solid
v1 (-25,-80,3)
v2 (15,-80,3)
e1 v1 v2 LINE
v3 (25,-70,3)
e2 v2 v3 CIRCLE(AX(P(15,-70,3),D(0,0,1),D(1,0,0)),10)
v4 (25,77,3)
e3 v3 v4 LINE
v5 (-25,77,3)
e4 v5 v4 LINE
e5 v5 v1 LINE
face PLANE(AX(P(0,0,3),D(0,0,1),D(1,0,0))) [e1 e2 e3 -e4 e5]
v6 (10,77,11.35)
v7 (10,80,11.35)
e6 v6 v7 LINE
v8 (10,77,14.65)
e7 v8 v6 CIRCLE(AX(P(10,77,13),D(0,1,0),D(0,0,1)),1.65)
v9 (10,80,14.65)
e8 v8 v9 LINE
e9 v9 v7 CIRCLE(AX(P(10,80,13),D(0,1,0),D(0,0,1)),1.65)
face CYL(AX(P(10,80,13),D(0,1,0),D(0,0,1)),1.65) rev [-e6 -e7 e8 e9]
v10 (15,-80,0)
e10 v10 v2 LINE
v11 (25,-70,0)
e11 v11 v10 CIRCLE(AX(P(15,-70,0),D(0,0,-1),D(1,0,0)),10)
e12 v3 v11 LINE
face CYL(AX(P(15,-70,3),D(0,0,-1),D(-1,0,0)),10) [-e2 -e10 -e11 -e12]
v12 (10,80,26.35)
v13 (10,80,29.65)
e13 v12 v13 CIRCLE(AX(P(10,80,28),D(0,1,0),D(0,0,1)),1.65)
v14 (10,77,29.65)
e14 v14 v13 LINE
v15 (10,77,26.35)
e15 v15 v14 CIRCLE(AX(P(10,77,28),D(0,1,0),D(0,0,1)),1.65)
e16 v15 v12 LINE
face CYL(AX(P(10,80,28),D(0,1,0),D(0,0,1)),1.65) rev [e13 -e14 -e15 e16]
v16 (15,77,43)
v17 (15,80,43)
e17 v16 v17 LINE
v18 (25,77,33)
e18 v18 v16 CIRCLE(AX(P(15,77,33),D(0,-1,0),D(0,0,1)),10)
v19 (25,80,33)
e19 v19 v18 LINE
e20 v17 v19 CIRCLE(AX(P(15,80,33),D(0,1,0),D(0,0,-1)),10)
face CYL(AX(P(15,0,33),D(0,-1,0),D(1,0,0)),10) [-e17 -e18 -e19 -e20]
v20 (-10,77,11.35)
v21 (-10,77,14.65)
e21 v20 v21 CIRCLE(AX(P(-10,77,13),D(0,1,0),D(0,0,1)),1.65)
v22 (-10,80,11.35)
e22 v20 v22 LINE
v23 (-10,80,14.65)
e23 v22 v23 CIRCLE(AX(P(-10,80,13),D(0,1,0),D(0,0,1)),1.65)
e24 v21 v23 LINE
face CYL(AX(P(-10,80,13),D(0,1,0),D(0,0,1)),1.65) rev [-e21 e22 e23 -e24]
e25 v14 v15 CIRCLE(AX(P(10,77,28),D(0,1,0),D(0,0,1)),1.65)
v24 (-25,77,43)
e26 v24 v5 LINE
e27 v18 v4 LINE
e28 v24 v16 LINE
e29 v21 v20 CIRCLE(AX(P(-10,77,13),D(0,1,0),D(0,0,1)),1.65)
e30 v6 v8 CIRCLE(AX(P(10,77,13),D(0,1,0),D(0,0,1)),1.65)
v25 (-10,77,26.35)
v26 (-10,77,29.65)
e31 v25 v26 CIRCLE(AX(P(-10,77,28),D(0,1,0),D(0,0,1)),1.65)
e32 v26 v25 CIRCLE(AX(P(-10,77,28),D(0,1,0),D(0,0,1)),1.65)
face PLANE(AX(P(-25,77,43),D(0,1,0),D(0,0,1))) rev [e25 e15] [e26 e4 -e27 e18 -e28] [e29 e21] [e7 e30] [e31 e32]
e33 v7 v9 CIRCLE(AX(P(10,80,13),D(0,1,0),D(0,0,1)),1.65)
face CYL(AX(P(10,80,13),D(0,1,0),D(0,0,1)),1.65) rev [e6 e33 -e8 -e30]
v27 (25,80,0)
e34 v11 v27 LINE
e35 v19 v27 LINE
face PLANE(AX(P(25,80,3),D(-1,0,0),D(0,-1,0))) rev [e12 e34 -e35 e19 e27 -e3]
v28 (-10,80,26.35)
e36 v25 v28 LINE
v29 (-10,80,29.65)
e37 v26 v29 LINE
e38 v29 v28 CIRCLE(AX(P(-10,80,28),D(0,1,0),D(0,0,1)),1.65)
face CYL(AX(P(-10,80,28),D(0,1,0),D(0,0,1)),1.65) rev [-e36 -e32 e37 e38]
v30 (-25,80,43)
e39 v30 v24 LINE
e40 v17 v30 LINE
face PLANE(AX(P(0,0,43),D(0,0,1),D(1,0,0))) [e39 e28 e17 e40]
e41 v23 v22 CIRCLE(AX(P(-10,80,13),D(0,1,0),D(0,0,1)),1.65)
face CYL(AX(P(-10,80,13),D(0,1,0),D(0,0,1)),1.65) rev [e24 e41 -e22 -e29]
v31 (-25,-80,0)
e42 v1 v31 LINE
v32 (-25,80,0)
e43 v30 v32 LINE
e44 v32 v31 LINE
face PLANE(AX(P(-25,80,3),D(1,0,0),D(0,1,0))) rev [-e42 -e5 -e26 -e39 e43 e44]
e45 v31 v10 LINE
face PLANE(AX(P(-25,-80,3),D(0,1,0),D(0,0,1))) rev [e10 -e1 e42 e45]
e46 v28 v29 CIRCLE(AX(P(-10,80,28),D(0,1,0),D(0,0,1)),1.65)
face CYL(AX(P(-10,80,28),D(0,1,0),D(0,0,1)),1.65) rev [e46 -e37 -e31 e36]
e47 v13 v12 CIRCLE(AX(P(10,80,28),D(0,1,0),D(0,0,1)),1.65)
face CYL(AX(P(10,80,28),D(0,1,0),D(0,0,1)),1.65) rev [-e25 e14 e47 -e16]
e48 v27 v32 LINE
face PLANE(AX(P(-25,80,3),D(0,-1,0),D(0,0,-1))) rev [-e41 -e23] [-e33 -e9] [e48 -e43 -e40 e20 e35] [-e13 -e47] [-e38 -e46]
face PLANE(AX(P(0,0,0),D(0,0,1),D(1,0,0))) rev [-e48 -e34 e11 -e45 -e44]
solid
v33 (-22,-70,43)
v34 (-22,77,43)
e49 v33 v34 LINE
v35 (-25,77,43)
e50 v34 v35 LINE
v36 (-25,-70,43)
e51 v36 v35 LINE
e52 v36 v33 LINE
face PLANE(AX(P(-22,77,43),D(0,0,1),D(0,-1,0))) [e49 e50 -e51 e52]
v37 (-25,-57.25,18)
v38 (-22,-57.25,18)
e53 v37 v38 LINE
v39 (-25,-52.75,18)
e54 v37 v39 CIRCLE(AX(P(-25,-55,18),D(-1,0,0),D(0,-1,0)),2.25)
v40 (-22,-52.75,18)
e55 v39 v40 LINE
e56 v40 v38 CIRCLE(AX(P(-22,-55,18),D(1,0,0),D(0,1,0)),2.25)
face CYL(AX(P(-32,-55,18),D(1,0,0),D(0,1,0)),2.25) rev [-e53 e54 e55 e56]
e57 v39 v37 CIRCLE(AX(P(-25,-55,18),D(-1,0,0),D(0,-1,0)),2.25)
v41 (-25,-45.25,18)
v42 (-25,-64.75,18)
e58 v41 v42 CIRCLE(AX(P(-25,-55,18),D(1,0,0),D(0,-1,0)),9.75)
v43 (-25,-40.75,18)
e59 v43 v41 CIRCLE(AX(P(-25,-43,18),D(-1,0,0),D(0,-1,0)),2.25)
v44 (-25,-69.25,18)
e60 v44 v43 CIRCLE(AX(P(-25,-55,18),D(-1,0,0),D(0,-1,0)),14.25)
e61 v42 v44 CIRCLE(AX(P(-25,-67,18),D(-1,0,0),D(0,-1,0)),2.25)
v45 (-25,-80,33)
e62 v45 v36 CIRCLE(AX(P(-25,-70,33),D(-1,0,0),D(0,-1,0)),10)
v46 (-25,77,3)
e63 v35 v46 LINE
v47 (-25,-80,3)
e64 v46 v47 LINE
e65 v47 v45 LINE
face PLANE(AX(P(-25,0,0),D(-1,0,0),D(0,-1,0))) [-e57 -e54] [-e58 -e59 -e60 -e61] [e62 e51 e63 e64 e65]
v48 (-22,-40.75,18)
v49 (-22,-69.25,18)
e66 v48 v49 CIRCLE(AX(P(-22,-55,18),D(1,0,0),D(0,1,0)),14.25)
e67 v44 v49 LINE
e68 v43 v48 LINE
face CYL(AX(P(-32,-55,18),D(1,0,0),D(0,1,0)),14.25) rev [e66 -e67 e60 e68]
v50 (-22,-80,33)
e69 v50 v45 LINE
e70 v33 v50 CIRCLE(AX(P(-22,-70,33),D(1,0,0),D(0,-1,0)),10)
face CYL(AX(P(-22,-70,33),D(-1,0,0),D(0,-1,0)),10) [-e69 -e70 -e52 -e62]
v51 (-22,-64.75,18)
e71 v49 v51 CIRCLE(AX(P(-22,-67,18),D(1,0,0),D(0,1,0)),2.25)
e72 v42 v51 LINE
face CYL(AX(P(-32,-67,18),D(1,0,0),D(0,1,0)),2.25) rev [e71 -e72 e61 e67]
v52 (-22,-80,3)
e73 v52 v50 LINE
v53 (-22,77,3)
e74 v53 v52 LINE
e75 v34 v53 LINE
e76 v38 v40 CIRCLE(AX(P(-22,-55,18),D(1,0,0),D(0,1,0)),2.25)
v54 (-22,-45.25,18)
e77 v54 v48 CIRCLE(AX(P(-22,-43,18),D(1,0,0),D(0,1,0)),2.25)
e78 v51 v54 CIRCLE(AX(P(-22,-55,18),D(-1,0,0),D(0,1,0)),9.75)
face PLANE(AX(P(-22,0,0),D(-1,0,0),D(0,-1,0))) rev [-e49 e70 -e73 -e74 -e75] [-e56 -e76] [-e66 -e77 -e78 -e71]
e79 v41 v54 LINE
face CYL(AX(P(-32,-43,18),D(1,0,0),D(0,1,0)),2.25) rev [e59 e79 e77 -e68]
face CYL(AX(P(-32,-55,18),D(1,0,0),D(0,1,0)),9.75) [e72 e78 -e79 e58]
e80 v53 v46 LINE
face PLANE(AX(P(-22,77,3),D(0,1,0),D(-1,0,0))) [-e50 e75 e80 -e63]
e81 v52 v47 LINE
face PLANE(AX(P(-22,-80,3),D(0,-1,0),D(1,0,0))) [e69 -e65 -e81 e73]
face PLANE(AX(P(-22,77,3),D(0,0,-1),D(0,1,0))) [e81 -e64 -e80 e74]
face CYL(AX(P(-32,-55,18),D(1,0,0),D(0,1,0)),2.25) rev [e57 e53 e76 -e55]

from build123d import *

# Parameters (mm, degrees)
SKETCH_1_W                  = 50
SKETCH_1_H                  = 160
EXTRUDE_1_DEPTH             = 3
SKETCH_2_W                  = 50
SKETCH_2_H                  = 3
EXTRUDE_2_DEPTH             = 40
SKETCH_5_W                  = 40
SKETCH_5_H                  = 157
EXTRUDE_3_DEPTH             = 3
SKETCH_6_R                  = 2.25
CUT_EXTRUDE_1_DEPTH         = 10
SKETCH_8_W                  = 1.65
SKETCH_8_H                  = 160
HOLE_WIZARD_M4_1_AT_2_COUNT = 2
HOLE_WIZARD_M4_1_AT_2_PITCH = 20
HOLE_WIZARD_M4_1_AT_3_COUNT = 2
HOLE_WIZARD_M4_1_AT_3_PITCH = 15
HOLE_WIZARD_M4_1_AT_4_COUNT = 2
HOLE_WIZARD_M4_1_AT_4_PITCH = 25
FILLET_1_R                  = 10
FILLET_2_R                  = 10


with BuildPart() as part:
    # 草图1 → 凸台-拉伸1 (new body)
    with BuildSketch(Plane.XY):
        Rectangle(SKETCH_1_W, SKETCH_1_H)
    extrude(amount=EXTRUDE_1_DEPTH)

    # 草图2 → 凸台-拉伸2 (add)
    with BuildSketch(Plane.XY.offset(3)):
        with Locations((0, 78.5)):
            Rectangle(SKETCH_2_W, SKETCH_2_H)
    extrude(amount=EXTRUDE_2_DEPTH)

    # 草图8 → M4 螺纹孔1 (revolve, cut)
    with BuildSketch(Plane(origin=(-10, 80, 13), x_dir=(0, 0, 1), z_dir=(1, 0, 0))):
        with Locations((0.825, 80)):
            Rectangle(SKETCH_8_W, SKETCH_8_H)
    hole_wizard_m4_1 = revolve(axis=Axis((-10, 86.35, 13), (0, -1, 0)), mode=Mode.SUBTRACT)

    # M4 螺纹孔1 at 2: M4 螺纹孔1 ×2
    with Locations(*[(i * HOLE_WIZARD_M4_1_AT_2_PITCH, 0, 0) for i in range(1, HOLE_WIZARD_M4_1_AT_2_COUNT)]):
        add(hole_wizard_m4_1, mode=Mode.SUBTRACT)

    # M4 螺纹孔1 at 3: M4 螺纹孔1 ×2
    with Locations(*[(0, 0, i * HOLE_WIZARD_M4_1_AT_3_PITCH) for i in range(1, HOLE_WIZARD_M4_1_AT_3_COUNT)]):
        add(hole_wizard_m4_1, mode=Mode.SUBTRACT)

    # M4 螺纹孔1 at 4: M4 螺纹孔1 ×2
    with Locations(*[Vector(0.8000000000000002, 0, 0.5999999999999999) * (i * HOLE_WIZARD_M4_1_AT_4_PITCH) for i in range(1, HOLE_WIZARD_M4_1_AT_4_COUNT)]):
        add(hole_wizard_m4_1, mode=Mode.SUBTRACT)

    # 圆角1
    fillet_1_edges = [part.edges().sort_by_distance(p)[0] for p in [
        (25, 78.5, 43),
        (25, -80, 1.5),
    ]]
    fillet(fillet_1_edges, radius=FILLET_1_R)


with BuildPart() as body_2:
    # 草图5 → 凸台-拉伸3 (new body)
    with BuildSketch(Plane.ZY.offset(25)):
        with Locations((23, -1.5)):
            Rectangle(SKETCH_5_W, SKETCH_5_H)
    extrude(amount=-EXTRUDE_3_DEPTH)

    # 草图6 → 切除-拉伸1 (cut)
    with BuildSketch(Plane(origin=(-22, 0, 0), x_dir=(0, 0, -1), z_dir=(1, 0, 0))):
        with Locations(Location((-18, -55, 0), (0, 0, 90))):
            Circle(SKETCH_6_R)
        with BuildLine():
            ThreePointArc((-18, -40.75), (-32.25, -55), (-18, -69.25))
            ThreePointArc((-18, -69.25), (-15.75, -67), (-18, -64.75))
            ThreePointArc((-18, -64.75), (-27.75, -55), (-18, -45.25))
            ThreePointArc((-18, -45.25), (-15.75, -43), (-18, -40.75))
        make_face()
    extrude(amount=-CUT_EXTRUDE_1_DEPTH, mode=Mode.SUBTRACT)

    # 圆角2
    fillet_2_edges = [body_2.edges().sort_by_distance(p)[0] for p in [
        (-23.5, -80, 43),
    ]]
    fillet(fillet_2_edges, radius=FILLET_2_R)


solid = Compound([part.part, body_2.part])
